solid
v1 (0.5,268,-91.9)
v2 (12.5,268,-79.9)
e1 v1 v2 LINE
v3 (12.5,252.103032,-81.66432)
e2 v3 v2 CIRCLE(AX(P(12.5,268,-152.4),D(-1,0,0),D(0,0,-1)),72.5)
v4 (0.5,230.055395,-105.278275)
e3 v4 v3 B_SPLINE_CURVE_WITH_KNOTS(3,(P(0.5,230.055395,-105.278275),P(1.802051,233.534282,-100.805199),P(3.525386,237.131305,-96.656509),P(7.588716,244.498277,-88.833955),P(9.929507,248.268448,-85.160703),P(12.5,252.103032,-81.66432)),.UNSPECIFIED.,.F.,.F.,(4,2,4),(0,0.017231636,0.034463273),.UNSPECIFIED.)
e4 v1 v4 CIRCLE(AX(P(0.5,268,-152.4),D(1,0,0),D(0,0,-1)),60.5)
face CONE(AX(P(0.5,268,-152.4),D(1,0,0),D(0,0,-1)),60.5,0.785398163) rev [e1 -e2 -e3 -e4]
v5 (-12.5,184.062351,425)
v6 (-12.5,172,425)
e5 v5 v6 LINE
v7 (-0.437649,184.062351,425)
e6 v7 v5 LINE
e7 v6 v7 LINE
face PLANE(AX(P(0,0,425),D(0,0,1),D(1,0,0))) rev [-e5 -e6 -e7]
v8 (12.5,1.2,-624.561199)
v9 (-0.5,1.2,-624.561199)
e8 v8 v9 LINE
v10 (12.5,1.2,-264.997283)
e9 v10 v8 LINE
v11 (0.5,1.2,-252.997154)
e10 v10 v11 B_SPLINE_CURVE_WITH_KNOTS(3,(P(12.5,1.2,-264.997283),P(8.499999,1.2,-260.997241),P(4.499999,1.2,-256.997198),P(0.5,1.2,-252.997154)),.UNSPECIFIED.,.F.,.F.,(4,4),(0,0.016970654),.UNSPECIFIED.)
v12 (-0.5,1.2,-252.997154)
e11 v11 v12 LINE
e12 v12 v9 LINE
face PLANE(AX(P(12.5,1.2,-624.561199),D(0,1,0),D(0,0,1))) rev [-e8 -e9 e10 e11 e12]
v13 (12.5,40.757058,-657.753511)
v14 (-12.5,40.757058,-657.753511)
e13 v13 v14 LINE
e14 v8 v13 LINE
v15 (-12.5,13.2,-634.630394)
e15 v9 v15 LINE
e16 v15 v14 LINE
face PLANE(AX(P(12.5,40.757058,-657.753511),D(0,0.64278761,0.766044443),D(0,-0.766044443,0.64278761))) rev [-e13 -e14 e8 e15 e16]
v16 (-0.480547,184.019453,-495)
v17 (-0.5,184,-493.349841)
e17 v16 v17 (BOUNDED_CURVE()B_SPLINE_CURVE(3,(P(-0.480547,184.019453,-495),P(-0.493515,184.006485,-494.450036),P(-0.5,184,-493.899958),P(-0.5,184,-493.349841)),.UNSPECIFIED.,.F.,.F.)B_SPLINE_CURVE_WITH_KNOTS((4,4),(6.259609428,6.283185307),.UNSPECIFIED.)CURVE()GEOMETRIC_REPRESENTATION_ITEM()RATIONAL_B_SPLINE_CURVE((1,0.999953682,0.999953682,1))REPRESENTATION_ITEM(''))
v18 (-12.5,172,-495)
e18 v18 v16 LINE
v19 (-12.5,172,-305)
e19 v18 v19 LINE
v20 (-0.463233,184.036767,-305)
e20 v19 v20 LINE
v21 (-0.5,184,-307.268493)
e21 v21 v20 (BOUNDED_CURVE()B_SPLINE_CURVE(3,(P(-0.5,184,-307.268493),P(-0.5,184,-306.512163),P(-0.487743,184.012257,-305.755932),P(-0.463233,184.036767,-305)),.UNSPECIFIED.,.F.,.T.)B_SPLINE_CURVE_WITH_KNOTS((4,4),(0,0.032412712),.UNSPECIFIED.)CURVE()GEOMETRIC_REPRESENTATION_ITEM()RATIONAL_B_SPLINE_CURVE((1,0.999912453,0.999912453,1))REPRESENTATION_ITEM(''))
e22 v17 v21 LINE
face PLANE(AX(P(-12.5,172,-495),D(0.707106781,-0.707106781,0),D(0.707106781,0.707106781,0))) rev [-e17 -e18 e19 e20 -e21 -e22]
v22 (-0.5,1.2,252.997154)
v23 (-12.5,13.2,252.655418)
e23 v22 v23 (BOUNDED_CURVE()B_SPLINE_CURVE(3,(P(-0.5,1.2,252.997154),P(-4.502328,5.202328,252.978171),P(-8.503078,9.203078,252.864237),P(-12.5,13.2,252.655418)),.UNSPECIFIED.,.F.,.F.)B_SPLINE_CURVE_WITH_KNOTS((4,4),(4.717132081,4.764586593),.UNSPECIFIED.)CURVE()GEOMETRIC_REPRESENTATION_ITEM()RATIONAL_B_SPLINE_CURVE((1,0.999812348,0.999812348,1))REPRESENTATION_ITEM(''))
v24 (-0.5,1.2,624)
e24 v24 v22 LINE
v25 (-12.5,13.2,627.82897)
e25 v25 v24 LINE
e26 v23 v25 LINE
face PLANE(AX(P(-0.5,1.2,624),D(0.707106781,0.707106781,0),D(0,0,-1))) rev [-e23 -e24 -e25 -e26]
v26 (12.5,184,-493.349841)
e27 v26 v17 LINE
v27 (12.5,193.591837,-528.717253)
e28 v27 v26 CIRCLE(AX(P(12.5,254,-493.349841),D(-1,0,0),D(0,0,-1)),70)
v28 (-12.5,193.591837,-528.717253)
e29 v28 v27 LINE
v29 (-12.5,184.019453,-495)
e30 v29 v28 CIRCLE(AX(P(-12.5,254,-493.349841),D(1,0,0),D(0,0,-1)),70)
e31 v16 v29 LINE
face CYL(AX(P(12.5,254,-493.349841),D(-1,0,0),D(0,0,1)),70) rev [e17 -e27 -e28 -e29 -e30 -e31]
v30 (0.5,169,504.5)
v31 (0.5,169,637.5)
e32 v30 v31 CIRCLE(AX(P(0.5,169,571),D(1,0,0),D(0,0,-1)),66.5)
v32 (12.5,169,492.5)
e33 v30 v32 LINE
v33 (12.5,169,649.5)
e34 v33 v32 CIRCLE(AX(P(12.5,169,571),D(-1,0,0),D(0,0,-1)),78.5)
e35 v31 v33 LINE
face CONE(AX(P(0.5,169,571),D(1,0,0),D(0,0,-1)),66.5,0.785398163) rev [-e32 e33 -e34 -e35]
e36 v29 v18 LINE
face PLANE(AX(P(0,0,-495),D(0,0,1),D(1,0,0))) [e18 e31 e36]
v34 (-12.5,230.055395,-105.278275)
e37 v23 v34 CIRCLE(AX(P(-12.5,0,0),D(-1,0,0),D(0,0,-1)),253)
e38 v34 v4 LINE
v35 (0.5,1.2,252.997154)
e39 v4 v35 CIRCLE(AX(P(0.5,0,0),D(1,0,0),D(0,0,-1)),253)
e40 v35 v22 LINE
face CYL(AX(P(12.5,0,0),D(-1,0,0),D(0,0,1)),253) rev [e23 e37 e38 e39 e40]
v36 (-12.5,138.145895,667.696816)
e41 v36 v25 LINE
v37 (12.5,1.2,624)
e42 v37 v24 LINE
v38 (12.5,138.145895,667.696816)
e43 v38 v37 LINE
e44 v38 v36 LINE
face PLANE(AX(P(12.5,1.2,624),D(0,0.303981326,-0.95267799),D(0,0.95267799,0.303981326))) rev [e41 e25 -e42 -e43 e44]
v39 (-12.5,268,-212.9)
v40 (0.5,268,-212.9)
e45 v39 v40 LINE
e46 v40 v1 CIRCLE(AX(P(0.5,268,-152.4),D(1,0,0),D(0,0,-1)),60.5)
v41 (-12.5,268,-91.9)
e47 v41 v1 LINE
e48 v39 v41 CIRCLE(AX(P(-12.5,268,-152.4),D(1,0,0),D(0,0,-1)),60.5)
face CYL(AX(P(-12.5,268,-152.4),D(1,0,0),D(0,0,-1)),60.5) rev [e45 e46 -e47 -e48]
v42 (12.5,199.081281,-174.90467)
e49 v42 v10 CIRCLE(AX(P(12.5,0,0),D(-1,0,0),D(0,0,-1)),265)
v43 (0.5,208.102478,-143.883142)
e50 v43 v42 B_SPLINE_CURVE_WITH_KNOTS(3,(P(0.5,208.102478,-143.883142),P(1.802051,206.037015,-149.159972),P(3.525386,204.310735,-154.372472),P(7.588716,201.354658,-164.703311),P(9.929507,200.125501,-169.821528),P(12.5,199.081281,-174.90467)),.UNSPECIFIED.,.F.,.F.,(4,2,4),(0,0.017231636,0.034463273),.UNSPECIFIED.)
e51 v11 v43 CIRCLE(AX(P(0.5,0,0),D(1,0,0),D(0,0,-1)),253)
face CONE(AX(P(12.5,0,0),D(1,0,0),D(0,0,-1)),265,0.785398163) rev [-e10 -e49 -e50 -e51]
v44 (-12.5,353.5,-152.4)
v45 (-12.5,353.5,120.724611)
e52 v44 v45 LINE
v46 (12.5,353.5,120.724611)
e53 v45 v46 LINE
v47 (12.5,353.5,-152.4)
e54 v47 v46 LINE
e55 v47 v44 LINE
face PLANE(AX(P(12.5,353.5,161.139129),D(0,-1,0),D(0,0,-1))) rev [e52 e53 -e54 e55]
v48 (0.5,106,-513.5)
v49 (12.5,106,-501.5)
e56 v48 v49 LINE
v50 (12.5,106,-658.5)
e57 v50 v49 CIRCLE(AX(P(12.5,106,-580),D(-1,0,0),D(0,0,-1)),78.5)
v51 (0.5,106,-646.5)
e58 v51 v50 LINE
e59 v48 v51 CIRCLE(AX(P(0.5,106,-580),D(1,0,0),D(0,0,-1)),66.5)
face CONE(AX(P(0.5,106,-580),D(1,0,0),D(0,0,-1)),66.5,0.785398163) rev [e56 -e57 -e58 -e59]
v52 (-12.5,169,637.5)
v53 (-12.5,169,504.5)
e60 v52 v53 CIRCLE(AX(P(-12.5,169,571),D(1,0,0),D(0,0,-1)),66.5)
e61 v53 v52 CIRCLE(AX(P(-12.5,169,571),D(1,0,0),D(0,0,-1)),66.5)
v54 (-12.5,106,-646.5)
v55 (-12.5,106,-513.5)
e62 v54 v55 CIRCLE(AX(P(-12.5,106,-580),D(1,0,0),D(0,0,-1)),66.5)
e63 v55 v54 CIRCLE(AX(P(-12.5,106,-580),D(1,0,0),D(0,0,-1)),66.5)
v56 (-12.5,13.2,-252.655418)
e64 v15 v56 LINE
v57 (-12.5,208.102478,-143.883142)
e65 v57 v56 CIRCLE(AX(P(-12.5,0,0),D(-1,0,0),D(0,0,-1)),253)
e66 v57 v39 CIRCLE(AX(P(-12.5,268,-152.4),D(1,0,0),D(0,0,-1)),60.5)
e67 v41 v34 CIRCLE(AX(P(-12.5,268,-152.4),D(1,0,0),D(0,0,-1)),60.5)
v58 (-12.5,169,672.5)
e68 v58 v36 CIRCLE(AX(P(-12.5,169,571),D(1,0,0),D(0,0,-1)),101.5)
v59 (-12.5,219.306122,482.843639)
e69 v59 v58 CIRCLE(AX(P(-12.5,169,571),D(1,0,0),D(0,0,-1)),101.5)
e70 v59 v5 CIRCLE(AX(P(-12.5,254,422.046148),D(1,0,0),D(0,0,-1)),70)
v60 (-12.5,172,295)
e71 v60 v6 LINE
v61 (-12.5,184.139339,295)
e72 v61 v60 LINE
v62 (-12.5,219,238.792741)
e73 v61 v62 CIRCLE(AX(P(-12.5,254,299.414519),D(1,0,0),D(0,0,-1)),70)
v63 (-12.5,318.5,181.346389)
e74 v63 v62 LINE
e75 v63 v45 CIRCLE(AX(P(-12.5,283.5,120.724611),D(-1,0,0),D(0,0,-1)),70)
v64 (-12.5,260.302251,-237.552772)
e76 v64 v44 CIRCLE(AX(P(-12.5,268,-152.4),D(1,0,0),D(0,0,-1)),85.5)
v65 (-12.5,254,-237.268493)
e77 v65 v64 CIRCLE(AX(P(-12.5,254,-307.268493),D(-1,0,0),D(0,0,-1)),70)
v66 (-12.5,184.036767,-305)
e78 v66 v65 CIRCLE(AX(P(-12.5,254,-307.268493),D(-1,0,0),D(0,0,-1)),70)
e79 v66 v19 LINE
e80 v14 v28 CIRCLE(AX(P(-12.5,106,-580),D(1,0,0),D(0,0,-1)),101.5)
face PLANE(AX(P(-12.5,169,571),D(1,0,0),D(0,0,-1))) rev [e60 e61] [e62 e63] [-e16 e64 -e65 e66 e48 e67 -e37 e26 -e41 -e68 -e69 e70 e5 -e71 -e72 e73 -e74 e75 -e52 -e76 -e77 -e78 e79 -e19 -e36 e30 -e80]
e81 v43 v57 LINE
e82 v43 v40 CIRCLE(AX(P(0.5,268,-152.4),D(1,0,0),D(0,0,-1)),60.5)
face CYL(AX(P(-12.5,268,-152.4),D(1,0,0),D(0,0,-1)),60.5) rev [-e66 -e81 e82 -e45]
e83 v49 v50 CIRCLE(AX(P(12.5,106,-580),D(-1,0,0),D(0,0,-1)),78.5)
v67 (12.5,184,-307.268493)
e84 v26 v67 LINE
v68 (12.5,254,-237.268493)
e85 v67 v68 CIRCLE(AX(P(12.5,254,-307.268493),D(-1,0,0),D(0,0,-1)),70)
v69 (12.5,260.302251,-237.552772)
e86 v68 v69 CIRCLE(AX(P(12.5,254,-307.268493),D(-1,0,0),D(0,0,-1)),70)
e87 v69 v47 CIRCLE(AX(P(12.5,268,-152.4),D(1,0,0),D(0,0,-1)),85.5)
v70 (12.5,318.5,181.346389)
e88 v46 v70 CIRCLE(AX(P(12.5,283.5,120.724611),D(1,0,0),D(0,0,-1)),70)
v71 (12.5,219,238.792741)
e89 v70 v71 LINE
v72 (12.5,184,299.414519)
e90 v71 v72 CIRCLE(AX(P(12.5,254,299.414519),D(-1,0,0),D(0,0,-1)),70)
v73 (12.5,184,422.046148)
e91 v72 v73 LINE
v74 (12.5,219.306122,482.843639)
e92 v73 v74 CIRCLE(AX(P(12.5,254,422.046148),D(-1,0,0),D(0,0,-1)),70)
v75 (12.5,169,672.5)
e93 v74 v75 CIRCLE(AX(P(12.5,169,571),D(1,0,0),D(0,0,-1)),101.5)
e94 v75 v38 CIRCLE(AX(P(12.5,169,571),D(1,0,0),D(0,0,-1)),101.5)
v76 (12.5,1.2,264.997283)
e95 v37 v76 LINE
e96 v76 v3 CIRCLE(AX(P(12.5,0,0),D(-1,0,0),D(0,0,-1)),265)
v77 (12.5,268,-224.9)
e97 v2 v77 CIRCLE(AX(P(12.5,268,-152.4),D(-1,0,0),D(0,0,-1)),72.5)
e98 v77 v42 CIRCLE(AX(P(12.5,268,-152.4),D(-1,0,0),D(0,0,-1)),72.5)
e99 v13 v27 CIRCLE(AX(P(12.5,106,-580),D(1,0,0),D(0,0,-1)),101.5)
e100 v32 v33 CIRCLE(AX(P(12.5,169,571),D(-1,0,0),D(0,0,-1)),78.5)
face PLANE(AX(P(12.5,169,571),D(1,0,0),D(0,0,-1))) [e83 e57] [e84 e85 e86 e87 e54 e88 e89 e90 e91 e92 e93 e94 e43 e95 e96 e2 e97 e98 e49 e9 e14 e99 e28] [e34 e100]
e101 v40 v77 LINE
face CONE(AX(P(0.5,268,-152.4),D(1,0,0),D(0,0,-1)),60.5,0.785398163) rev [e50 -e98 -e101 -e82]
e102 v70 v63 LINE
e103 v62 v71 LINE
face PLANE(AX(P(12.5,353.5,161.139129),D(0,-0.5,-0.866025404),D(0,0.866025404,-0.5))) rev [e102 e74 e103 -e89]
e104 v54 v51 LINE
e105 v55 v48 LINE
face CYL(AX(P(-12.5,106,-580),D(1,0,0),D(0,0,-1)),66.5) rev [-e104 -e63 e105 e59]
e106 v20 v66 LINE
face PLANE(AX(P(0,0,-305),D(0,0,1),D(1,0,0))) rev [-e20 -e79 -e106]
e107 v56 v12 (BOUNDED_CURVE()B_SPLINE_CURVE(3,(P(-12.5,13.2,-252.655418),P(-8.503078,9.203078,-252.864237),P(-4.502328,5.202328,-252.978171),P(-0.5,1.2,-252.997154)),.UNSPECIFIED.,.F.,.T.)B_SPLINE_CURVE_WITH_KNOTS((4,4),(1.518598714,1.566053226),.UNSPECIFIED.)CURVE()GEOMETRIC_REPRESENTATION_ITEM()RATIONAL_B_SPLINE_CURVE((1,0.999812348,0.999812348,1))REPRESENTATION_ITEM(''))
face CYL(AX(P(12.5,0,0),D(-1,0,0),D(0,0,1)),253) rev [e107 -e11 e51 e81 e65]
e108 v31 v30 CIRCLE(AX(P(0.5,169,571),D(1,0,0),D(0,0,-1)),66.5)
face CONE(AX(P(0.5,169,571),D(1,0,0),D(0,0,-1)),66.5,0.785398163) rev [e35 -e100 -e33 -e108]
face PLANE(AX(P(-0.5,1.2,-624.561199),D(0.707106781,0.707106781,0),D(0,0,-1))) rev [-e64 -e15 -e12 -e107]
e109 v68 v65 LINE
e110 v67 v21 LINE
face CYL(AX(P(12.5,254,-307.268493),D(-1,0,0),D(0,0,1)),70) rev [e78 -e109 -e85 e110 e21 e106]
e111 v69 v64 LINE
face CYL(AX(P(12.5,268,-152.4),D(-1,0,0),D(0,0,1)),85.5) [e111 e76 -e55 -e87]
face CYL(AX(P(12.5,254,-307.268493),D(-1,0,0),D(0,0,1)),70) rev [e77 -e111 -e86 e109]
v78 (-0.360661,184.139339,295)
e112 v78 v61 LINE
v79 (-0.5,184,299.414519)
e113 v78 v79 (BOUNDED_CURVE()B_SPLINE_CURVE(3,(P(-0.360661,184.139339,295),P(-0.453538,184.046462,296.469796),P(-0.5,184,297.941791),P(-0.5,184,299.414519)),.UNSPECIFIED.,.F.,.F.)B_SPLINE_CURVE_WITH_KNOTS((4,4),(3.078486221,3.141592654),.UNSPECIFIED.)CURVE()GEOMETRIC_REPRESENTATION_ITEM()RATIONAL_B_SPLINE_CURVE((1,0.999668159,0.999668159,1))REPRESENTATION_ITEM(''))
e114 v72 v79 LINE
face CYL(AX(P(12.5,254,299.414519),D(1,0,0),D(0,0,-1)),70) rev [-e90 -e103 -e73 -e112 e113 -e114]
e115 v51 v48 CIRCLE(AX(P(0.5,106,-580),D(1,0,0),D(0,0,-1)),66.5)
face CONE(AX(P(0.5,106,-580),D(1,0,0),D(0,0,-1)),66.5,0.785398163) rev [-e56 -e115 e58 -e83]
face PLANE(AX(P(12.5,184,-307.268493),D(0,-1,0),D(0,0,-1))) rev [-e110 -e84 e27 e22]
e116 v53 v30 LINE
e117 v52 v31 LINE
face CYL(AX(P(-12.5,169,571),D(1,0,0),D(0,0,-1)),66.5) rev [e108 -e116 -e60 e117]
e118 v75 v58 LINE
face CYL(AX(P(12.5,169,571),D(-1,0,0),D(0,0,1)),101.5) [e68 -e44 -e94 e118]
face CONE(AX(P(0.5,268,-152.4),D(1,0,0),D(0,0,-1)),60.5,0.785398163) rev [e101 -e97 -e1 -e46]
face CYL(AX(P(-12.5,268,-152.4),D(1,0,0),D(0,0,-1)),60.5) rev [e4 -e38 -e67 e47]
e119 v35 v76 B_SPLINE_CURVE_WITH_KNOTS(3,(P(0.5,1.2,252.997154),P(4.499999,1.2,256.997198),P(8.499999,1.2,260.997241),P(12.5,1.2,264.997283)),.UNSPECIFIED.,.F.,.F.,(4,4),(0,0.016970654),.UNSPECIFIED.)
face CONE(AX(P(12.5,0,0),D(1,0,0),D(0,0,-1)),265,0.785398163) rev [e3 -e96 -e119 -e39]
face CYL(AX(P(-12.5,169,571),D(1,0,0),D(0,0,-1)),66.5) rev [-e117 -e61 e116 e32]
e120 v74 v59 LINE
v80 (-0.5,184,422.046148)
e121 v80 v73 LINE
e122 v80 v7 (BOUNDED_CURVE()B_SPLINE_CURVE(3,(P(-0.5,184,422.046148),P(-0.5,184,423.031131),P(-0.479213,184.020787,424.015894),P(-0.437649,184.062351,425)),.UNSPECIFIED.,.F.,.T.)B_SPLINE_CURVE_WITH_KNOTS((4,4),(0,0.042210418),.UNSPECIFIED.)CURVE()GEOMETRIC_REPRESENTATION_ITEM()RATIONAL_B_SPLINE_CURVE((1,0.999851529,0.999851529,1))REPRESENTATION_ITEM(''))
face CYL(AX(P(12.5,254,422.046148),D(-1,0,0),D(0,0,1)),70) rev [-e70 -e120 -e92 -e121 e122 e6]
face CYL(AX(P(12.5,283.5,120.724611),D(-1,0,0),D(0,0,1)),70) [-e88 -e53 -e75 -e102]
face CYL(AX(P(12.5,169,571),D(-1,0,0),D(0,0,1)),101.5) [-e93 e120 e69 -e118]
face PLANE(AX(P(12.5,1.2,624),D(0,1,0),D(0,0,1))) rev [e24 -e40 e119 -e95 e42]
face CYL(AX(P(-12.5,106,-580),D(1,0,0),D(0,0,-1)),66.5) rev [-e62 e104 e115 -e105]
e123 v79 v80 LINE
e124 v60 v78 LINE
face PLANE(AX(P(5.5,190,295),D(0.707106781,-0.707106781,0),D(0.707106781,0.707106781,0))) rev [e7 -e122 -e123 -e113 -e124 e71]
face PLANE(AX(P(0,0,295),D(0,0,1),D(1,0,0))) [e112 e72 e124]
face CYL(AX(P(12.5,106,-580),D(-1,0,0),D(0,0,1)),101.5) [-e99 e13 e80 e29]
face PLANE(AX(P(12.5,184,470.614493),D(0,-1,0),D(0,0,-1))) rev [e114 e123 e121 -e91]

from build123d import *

# Parameters (mm, degrees)
BOSS_EXTRUDE1_DEPTH     = 12.5
CUT_EXTRUDE1_DEPTH      = 768.828594154
CUT_EXTRUDE1_DEPTH_BACK = 768.828594154
SKETCH2_R               = 60.5
SKETCH2_R_2             = 66.5
FILLET1_R               = 70
CHAMFER1_SIZE           = 12
CHAMFER2_SIZE           = 12
CUT_EXTRUDE2_DEPTH      = 65
CUT_EXTRUDE3_DEPTH      = 95


with BuildPart() as part:
    # Sketch1 → Boss-Extrude1 (new, symmetric)
    with BuildSketch(Plane(origin=(0, 0, 0), x_dir=(0, 0, -1), z_dir=(1, 0, 0))):
        with BuildLine():
            Line((-161.139129372, 353.5), (152.4, 353.5))
            ThreePointArc((152.4, 353.5), (215.520549571, 325.671884154), (237.552772458, 260.302250804))
            ThreePointArc((237.552772458, 260.302250804), (255.590849676, 206.783252739), (307.268492599, 184))
            Line((307.268492599, 184), (515.051943832, 184))
            ThreePointArc((515.051943832, 184), (651.90709321, 177.635326105), (657.753510977, 40.757057617))
            Line((657.753510977, 40.757057617), (624.56119852, 1.2))
            Line((624.56119852, 1.2), (252.997154134, 1.2))
            ThreePointArc((252.997154134, 1.2), (0, 253), (-252.997154134, 1.2))
            Line((-252.997154134, 1.2), (-624, 1.2))
            Line((-624, 1.2), (-667.696816027, 138.145895408))
            ThreePointArc((-667.696816027, 138.145895408), (-594.001115997, 267.859489493), (-470.614493078, 184))
            Line((-470.614493078, 184), (-259, 184))
            Line((-259, 184), (-161.139129372, 353.5))
        make_face()
    extrude(amount=BOSS_EXTRUDE1_DEPTH, both=True)

    # Sketch2 → Cut-Extrude1 (cut, two sides: drawn at the far end of the back side and taken through both)
    with BuildSketch(Plane(origin=(0, 0, 0), x_dir=(0, 0, -1), z_dir=(1, 0, 0)).offset(-CUT_EXTRUDE1_DEPTH_BACK)):
        with Locations((152.4, 268)):
            Circle(SKETCH2_R)
        with Locations((-571, 169)):
            Circle(SKETCH2_R_2)
        with Locations((580, 106)):
            Circle(SKETCH2_R_2)
    extrude(amount=CUT_EXTRUDE1_DEPTH + CUT_EXTRUDE1_DEPTH_BACK, mode=Mode.SUBTRACT)

    # Fillet1
    fillet1_edges = [part.edges().sort_by_distance(p)[0] for p in [
        (0, 184, 470.614493078),
        (0, 184, 259),
        (0, 353.5, 161.139129372),
        (0, 184, -515.051943832),
    ]]
    fillet(fillet1_edges, radius=FILLET1_R)

    # Chamfer1
    chamfer1_edges = [part.edges().sort_by_distance(p)[0] for p in [
        (12.5, 213.213707904, 136.194400626),
        (12.5, 118.018425376, -223.787066811),
        (12.5, 320.591390839, -182.306447626),
        (12.5, 169, 637.5),
        (12.5, 106, -513.5),
    ]]
    chamfer(chamfer1_edges, length=CHAMFER1_SIZE)

    # Chamfer2
    chamfer2_edges = [part.edges().sort_by_distance(p)[0] for p in [
        (-12.5, 1.2, -438.779176327),
        (-12.5, 1.2, 438.498577067),
    ]]
    chamfer(chamfer2_edges, length=CHAMFER2_SIZE)

    # Sketch3 → Cut-Extrude2 (cut, symmetric)
    with BuildSketch(Plane.XY.offset(360)):
        Polygon((5.5, 190), (-12.5, 172), (-12.5, 190), align=None)
    extrude(amount=CUT_EXTRUDE2_DEPTH, both=True, mode=Mode.SUBTRACT)

    # Sketch4 → Cut-Extrude3 (cut, symmetric)
    with BuildSketch(Plane.XY.offset(-400)):
        Polygon((-12.5, 172), (5.5, 190), (-12.5, 190), align=None)
    extrude(amount=CUT_EXTRUDE3_DEPTH, both=True, mode=Mode.SUBTRACT)


solid = part.part
